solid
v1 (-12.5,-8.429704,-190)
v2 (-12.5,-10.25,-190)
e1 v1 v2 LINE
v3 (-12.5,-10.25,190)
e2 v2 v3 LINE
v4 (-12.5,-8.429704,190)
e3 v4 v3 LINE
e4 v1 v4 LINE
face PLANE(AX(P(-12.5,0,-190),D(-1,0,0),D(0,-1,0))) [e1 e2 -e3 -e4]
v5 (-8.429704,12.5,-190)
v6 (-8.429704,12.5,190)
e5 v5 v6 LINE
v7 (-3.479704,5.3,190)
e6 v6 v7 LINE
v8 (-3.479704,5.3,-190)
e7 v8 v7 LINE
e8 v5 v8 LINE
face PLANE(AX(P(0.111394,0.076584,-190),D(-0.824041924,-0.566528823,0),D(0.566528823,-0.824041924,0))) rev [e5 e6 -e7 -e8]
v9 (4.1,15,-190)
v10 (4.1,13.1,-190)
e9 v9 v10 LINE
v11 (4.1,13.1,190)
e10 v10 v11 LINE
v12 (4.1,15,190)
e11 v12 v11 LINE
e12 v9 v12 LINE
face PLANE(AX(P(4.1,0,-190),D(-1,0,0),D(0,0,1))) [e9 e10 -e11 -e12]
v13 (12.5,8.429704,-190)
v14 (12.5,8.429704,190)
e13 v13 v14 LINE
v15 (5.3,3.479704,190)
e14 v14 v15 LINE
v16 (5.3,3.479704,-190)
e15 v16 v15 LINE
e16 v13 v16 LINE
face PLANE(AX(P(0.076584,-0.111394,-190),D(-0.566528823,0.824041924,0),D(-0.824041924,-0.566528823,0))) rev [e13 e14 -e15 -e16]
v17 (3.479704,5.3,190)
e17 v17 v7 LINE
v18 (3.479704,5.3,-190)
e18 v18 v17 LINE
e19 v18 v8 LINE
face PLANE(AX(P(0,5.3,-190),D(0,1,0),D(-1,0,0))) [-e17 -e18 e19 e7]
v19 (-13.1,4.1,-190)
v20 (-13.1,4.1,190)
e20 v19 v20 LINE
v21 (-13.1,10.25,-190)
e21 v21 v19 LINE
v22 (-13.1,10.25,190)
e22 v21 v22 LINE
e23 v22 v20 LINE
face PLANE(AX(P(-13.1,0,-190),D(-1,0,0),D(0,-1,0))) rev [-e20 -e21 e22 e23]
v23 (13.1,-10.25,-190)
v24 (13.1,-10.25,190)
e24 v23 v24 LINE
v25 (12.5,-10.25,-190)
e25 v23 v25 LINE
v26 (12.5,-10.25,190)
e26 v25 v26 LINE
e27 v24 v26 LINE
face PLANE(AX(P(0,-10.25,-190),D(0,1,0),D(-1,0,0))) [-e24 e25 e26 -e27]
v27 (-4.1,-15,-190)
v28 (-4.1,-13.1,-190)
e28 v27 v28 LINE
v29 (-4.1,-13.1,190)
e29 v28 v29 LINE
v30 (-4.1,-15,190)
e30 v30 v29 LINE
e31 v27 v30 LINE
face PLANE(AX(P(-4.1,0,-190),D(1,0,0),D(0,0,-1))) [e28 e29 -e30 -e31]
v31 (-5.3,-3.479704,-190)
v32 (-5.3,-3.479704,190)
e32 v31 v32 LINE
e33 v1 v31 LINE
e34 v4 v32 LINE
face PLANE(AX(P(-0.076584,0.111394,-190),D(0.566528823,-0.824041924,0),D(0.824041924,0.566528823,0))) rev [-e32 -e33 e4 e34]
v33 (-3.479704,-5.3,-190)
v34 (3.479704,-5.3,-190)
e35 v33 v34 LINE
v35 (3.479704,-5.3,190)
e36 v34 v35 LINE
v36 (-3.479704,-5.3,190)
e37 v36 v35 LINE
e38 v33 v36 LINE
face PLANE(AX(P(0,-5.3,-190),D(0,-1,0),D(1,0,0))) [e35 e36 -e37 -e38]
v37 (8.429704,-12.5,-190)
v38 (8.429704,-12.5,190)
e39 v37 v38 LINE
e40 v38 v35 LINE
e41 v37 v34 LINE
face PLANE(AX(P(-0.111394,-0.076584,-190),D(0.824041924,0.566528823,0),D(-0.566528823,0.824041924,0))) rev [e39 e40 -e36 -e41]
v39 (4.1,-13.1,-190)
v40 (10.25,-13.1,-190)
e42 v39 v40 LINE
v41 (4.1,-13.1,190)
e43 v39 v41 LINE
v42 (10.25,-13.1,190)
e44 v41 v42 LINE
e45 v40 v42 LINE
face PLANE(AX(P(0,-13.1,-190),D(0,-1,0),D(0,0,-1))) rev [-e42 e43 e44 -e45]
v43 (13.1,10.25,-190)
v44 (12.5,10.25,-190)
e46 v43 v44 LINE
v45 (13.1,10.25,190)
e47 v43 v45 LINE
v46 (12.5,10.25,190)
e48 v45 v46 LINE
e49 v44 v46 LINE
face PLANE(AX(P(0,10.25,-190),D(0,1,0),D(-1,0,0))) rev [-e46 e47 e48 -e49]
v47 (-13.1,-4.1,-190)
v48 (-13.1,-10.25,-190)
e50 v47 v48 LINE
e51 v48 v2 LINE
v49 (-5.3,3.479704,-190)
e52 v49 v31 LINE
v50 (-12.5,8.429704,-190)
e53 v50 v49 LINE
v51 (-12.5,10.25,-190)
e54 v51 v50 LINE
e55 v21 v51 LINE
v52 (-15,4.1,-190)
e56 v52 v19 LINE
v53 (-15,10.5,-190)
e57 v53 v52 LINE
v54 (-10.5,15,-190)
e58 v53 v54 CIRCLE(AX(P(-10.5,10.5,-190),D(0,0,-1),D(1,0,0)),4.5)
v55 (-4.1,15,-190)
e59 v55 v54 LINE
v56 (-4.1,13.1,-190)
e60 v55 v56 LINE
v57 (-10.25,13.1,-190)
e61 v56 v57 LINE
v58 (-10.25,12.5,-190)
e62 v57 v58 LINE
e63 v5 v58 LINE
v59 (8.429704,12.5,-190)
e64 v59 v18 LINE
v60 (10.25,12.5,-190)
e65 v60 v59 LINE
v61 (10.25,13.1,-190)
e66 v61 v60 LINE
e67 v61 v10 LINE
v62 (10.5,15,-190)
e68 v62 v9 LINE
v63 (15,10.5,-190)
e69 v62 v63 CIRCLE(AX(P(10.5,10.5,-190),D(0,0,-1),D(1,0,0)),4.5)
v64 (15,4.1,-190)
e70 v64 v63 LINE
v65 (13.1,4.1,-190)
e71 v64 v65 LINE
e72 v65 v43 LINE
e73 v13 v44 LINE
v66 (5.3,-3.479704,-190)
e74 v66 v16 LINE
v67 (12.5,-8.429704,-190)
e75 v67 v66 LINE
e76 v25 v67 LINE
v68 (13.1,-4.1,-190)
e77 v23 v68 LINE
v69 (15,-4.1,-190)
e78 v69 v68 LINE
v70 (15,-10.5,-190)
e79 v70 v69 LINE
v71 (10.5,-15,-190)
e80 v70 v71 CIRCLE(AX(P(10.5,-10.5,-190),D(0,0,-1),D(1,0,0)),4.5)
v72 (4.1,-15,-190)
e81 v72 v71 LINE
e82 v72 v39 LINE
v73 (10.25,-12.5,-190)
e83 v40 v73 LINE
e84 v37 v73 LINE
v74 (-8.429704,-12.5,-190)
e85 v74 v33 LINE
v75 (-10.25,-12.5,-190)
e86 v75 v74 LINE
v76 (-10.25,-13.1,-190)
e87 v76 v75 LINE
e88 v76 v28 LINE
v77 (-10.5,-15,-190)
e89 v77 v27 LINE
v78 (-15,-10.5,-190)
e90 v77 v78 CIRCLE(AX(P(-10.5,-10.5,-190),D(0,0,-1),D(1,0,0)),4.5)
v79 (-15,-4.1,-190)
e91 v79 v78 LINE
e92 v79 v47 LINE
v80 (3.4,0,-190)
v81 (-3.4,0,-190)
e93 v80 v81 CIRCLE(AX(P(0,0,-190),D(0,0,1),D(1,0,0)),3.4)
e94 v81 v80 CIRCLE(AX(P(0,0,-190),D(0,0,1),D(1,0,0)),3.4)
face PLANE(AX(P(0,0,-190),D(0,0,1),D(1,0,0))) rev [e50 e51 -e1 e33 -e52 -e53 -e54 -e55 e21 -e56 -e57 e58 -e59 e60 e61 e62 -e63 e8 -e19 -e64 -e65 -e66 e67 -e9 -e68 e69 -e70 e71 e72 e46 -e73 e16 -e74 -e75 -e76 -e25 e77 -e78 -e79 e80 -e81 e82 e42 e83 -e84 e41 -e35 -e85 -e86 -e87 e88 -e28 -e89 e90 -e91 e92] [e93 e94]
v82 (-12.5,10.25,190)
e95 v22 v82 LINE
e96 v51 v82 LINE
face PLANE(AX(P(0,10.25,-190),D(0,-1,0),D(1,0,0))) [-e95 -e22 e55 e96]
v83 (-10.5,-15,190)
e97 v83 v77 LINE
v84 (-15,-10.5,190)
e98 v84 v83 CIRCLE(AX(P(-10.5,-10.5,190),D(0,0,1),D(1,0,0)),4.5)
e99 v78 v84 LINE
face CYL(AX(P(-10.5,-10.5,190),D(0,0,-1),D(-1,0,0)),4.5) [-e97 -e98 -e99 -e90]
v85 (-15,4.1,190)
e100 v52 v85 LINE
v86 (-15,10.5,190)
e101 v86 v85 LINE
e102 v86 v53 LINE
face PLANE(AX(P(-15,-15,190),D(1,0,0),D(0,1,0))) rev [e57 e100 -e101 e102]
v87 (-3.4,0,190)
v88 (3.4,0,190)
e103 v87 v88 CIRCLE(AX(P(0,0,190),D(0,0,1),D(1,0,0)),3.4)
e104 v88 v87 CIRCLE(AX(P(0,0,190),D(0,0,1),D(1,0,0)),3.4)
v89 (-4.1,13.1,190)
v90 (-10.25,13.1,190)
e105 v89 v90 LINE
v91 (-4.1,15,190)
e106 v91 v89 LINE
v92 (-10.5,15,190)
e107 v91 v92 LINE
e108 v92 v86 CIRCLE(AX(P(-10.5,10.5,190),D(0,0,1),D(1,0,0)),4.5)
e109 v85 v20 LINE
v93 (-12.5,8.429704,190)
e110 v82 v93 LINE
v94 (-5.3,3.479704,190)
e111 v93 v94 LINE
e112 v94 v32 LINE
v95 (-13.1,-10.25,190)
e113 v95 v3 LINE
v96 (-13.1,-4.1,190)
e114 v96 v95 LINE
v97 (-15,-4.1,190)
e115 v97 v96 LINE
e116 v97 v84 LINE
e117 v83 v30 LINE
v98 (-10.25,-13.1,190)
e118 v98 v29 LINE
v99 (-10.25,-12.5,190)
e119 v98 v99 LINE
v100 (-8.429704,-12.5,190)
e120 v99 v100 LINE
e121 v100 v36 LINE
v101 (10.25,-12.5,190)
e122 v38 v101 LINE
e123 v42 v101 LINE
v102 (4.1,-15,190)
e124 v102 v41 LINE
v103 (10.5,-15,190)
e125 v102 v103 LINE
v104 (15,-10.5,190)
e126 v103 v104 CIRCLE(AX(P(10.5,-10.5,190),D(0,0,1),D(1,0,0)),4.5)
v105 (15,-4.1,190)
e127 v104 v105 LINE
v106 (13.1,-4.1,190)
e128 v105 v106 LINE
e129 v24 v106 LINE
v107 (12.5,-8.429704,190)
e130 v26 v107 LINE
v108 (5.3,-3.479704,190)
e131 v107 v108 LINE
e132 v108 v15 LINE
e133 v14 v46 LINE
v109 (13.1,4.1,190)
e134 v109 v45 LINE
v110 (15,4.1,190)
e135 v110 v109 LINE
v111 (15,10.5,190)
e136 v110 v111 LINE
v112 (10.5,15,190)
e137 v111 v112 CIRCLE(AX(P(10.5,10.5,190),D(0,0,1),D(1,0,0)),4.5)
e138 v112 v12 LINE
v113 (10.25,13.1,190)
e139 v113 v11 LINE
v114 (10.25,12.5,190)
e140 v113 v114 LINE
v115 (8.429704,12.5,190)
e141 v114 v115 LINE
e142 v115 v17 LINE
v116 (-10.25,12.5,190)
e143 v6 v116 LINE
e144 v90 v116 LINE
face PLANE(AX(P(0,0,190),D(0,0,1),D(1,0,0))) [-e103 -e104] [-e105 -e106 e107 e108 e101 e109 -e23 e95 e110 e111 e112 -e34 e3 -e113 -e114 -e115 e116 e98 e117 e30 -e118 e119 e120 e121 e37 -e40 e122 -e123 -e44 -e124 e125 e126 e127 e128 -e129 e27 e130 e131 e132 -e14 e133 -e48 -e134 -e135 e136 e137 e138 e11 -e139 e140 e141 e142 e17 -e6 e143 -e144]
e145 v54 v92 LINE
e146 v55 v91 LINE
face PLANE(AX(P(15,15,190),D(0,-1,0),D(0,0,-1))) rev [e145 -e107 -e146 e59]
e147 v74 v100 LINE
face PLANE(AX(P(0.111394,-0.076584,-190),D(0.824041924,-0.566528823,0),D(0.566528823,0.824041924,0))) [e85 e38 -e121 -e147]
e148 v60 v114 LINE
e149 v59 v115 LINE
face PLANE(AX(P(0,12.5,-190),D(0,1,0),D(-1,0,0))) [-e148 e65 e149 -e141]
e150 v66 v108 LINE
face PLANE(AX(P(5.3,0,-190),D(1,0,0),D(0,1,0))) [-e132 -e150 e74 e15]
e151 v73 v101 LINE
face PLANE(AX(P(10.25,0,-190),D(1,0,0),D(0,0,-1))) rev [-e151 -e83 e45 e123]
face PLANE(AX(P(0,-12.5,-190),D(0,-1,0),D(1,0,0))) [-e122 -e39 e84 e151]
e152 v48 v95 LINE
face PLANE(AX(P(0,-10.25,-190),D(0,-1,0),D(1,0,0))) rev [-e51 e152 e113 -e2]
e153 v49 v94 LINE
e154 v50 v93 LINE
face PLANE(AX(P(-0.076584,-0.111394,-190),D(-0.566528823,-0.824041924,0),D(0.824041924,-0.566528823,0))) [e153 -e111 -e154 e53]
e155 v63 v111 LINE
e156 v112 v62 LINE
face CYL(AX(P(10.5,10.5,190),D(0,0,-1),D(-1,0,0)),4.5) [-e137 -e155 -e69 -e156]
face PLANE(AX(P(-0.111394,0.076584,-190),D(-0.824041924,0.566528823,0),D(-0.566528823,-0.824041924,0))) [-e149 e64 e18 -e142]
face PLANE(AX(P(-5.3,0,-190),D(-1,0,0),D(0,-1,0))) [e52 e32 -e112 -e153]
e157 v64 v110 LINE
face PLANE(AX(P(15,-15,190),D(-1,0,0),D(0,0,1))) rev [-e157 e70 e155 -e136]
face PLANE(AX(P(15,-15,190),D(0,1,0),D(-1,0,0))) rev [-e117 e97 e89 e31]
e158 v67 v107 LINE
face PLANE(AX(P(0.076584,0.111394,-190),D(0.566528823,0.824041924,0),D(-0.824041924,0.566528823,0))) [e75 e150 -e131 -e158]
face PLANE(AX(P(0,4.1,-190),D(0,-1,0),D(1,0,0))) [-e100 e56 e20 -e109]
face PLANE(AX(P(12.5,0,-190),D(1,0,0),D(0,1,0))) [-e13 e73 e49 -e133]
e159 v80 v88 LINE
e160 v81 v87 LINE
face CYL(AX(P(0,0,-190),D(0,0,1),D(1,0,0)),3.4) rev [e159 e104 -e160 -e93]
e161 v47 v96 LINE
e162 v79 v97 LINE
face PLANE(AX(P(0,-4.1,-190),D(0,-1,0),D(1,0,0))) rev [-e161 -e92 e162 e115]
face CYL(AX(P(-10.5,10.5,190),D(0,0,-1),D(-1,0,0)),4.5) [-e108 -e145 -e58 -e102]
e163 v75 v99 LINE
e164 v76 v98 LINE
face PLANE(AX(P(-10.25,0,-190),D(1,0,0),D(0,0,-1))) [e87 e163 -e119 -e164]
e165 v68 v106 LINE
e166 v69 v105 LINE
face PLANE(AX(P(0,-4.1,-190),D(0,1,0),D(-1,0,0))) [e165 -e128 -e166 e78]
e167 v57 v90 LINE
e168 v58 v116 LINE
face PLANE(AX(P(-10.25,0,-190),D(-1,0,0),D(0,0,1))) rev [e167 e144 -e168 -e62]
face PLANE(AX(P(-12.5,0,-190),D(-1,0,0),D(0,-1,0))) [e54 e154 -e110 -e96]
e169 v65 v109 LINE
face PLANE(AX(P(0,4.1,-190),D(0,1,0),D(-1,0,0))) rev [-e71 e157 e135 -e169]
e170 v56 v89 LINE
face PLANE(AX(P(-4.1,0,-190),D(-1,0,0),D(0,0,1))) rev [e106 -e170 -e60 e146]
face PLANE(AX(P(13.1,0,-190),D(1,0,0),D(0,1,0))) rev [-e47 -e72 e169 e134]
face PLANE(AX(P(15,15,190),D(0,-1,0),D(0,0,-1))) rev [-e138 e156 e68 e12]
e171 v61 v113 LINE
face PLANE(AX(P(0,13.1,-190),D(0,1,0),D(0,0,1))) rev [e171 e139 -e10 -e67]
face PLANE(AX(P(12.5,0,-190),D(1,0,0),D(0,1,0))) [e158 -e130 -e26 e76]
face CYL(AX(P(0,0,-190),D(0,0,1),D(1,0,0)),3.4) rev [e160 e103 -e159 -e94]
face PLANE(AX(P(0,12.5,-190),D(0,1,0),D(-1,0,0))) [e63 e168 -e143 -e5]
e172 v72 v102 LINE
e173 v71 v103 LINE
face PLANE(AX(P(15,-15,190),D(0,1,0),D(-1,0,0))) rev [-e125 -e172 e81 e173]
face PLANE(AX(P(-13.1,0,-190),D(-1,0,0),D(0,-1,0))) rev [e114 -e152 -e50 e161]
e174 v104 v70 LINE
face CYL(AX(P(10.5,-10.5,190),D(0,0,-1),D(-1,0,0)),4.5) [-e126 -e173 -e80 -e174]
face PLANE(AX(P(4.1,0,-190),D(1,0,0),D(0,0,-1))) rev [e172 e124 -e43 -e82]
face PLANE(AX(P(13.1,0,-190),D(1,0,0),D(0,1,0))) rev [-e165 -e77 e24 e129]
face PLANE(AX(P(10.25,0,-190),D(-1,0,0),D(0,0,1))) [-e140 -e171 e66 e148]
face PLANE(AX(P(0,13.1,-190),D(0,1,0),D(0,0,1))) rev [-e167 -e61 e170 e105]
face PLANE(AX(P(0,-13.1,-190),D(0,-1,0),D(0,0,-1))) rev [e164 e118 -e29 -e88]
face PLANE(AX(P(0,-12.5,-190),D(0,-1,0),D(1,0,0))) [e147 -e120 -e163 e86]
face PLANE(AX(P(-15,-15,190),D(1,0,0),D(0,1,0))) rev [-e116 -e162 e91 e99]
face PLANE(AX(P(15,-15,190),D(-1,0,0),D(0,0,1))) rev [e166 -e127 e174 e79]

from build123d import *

# Parameters (mm, degrees)
SKETCH_1_W               = 30
SKETCH_1_H               = 30
EXTRUDE_1_DEPTH          = 190
FILLET_1_R               = 4.5
SKETCH_2_W               = 8.2
SKETCH_2_H               = 0.3
SKETCH_2_H_2             = 1.9
SKETCH_2_R               = 3.4
CUT_EXTRUDE_1_DEPTH      = 381.59164468
PATTERN_CIRCULAR_1_COUNT = 4


with BuildPart() as part:
    # 草图1 → 凸台-拉伸1 (new, symmetric)
    with BuildSketch(Plane.XY):
        Rectangle(SKETCH_1_W, SKETCH_1_H)
    extrude(amount=EXTRUDE_1_DEPTH, both=True)

    # 圆角1
    fillet_1_edges = [part.edges().sort_by_distance(p)[0] for p in [
        (-15, 15, 0),
        (15, 15, 0),
        (15, -15, 0),
        (-15, -15, 0),
    ]]
    fillet(fillet_1_edges, radius=FILLET_1_R)

    # 草图2 → 切除-拉伸1 (cut, through all)
    with BuildSketch(Plane.XY.offset(190)):
        with Locations((0, 12.95)):
            Rectangle(SKETCH_2_W, SKETCH_2_H)
        with Locations((0, 14.05)):
            Rectangle(SKETCH_2_W, SKETCH_2_H_2)
        Polygon((10.25, 13.1), (4.1, 13.1), (4.1, 12.8), (-4.1, 12.8), (-4.1, 13.1), (-10.25, 13.1), (-10.25, 12.5), (-8.429704265, 12.5), (8.429704265, 12.5), (10.25, 12.5), align=None)
        Polygon((3.479704265, 5.3), (8.429704265, 12.5), (-8.429704265, 12.5), (-3.479704265, 5.3), align=None)
        Circle(SKETCH_2_R)
    cut_extrude_1 = extrude(amount=-CUT_EXTRUDE_1_DEPTH, mode=Mode.SUBTRACT)

    # 阵列(圆周)1: 切除-拉伸1 ×4 about axis
    pattern_circular_1_axis = Axis((0, 0, 0), (0, 0, 1))
    for i in range(1, PATTERN_CIRCULAR_1_COUNT):
        add(cut_extrude_1.rotate(pattern_circular_1_axis, i * 360 / PATTERN_CIRCULAR_1_COUNT), mode=Mode.SUBTRACT)


solid = part.part
